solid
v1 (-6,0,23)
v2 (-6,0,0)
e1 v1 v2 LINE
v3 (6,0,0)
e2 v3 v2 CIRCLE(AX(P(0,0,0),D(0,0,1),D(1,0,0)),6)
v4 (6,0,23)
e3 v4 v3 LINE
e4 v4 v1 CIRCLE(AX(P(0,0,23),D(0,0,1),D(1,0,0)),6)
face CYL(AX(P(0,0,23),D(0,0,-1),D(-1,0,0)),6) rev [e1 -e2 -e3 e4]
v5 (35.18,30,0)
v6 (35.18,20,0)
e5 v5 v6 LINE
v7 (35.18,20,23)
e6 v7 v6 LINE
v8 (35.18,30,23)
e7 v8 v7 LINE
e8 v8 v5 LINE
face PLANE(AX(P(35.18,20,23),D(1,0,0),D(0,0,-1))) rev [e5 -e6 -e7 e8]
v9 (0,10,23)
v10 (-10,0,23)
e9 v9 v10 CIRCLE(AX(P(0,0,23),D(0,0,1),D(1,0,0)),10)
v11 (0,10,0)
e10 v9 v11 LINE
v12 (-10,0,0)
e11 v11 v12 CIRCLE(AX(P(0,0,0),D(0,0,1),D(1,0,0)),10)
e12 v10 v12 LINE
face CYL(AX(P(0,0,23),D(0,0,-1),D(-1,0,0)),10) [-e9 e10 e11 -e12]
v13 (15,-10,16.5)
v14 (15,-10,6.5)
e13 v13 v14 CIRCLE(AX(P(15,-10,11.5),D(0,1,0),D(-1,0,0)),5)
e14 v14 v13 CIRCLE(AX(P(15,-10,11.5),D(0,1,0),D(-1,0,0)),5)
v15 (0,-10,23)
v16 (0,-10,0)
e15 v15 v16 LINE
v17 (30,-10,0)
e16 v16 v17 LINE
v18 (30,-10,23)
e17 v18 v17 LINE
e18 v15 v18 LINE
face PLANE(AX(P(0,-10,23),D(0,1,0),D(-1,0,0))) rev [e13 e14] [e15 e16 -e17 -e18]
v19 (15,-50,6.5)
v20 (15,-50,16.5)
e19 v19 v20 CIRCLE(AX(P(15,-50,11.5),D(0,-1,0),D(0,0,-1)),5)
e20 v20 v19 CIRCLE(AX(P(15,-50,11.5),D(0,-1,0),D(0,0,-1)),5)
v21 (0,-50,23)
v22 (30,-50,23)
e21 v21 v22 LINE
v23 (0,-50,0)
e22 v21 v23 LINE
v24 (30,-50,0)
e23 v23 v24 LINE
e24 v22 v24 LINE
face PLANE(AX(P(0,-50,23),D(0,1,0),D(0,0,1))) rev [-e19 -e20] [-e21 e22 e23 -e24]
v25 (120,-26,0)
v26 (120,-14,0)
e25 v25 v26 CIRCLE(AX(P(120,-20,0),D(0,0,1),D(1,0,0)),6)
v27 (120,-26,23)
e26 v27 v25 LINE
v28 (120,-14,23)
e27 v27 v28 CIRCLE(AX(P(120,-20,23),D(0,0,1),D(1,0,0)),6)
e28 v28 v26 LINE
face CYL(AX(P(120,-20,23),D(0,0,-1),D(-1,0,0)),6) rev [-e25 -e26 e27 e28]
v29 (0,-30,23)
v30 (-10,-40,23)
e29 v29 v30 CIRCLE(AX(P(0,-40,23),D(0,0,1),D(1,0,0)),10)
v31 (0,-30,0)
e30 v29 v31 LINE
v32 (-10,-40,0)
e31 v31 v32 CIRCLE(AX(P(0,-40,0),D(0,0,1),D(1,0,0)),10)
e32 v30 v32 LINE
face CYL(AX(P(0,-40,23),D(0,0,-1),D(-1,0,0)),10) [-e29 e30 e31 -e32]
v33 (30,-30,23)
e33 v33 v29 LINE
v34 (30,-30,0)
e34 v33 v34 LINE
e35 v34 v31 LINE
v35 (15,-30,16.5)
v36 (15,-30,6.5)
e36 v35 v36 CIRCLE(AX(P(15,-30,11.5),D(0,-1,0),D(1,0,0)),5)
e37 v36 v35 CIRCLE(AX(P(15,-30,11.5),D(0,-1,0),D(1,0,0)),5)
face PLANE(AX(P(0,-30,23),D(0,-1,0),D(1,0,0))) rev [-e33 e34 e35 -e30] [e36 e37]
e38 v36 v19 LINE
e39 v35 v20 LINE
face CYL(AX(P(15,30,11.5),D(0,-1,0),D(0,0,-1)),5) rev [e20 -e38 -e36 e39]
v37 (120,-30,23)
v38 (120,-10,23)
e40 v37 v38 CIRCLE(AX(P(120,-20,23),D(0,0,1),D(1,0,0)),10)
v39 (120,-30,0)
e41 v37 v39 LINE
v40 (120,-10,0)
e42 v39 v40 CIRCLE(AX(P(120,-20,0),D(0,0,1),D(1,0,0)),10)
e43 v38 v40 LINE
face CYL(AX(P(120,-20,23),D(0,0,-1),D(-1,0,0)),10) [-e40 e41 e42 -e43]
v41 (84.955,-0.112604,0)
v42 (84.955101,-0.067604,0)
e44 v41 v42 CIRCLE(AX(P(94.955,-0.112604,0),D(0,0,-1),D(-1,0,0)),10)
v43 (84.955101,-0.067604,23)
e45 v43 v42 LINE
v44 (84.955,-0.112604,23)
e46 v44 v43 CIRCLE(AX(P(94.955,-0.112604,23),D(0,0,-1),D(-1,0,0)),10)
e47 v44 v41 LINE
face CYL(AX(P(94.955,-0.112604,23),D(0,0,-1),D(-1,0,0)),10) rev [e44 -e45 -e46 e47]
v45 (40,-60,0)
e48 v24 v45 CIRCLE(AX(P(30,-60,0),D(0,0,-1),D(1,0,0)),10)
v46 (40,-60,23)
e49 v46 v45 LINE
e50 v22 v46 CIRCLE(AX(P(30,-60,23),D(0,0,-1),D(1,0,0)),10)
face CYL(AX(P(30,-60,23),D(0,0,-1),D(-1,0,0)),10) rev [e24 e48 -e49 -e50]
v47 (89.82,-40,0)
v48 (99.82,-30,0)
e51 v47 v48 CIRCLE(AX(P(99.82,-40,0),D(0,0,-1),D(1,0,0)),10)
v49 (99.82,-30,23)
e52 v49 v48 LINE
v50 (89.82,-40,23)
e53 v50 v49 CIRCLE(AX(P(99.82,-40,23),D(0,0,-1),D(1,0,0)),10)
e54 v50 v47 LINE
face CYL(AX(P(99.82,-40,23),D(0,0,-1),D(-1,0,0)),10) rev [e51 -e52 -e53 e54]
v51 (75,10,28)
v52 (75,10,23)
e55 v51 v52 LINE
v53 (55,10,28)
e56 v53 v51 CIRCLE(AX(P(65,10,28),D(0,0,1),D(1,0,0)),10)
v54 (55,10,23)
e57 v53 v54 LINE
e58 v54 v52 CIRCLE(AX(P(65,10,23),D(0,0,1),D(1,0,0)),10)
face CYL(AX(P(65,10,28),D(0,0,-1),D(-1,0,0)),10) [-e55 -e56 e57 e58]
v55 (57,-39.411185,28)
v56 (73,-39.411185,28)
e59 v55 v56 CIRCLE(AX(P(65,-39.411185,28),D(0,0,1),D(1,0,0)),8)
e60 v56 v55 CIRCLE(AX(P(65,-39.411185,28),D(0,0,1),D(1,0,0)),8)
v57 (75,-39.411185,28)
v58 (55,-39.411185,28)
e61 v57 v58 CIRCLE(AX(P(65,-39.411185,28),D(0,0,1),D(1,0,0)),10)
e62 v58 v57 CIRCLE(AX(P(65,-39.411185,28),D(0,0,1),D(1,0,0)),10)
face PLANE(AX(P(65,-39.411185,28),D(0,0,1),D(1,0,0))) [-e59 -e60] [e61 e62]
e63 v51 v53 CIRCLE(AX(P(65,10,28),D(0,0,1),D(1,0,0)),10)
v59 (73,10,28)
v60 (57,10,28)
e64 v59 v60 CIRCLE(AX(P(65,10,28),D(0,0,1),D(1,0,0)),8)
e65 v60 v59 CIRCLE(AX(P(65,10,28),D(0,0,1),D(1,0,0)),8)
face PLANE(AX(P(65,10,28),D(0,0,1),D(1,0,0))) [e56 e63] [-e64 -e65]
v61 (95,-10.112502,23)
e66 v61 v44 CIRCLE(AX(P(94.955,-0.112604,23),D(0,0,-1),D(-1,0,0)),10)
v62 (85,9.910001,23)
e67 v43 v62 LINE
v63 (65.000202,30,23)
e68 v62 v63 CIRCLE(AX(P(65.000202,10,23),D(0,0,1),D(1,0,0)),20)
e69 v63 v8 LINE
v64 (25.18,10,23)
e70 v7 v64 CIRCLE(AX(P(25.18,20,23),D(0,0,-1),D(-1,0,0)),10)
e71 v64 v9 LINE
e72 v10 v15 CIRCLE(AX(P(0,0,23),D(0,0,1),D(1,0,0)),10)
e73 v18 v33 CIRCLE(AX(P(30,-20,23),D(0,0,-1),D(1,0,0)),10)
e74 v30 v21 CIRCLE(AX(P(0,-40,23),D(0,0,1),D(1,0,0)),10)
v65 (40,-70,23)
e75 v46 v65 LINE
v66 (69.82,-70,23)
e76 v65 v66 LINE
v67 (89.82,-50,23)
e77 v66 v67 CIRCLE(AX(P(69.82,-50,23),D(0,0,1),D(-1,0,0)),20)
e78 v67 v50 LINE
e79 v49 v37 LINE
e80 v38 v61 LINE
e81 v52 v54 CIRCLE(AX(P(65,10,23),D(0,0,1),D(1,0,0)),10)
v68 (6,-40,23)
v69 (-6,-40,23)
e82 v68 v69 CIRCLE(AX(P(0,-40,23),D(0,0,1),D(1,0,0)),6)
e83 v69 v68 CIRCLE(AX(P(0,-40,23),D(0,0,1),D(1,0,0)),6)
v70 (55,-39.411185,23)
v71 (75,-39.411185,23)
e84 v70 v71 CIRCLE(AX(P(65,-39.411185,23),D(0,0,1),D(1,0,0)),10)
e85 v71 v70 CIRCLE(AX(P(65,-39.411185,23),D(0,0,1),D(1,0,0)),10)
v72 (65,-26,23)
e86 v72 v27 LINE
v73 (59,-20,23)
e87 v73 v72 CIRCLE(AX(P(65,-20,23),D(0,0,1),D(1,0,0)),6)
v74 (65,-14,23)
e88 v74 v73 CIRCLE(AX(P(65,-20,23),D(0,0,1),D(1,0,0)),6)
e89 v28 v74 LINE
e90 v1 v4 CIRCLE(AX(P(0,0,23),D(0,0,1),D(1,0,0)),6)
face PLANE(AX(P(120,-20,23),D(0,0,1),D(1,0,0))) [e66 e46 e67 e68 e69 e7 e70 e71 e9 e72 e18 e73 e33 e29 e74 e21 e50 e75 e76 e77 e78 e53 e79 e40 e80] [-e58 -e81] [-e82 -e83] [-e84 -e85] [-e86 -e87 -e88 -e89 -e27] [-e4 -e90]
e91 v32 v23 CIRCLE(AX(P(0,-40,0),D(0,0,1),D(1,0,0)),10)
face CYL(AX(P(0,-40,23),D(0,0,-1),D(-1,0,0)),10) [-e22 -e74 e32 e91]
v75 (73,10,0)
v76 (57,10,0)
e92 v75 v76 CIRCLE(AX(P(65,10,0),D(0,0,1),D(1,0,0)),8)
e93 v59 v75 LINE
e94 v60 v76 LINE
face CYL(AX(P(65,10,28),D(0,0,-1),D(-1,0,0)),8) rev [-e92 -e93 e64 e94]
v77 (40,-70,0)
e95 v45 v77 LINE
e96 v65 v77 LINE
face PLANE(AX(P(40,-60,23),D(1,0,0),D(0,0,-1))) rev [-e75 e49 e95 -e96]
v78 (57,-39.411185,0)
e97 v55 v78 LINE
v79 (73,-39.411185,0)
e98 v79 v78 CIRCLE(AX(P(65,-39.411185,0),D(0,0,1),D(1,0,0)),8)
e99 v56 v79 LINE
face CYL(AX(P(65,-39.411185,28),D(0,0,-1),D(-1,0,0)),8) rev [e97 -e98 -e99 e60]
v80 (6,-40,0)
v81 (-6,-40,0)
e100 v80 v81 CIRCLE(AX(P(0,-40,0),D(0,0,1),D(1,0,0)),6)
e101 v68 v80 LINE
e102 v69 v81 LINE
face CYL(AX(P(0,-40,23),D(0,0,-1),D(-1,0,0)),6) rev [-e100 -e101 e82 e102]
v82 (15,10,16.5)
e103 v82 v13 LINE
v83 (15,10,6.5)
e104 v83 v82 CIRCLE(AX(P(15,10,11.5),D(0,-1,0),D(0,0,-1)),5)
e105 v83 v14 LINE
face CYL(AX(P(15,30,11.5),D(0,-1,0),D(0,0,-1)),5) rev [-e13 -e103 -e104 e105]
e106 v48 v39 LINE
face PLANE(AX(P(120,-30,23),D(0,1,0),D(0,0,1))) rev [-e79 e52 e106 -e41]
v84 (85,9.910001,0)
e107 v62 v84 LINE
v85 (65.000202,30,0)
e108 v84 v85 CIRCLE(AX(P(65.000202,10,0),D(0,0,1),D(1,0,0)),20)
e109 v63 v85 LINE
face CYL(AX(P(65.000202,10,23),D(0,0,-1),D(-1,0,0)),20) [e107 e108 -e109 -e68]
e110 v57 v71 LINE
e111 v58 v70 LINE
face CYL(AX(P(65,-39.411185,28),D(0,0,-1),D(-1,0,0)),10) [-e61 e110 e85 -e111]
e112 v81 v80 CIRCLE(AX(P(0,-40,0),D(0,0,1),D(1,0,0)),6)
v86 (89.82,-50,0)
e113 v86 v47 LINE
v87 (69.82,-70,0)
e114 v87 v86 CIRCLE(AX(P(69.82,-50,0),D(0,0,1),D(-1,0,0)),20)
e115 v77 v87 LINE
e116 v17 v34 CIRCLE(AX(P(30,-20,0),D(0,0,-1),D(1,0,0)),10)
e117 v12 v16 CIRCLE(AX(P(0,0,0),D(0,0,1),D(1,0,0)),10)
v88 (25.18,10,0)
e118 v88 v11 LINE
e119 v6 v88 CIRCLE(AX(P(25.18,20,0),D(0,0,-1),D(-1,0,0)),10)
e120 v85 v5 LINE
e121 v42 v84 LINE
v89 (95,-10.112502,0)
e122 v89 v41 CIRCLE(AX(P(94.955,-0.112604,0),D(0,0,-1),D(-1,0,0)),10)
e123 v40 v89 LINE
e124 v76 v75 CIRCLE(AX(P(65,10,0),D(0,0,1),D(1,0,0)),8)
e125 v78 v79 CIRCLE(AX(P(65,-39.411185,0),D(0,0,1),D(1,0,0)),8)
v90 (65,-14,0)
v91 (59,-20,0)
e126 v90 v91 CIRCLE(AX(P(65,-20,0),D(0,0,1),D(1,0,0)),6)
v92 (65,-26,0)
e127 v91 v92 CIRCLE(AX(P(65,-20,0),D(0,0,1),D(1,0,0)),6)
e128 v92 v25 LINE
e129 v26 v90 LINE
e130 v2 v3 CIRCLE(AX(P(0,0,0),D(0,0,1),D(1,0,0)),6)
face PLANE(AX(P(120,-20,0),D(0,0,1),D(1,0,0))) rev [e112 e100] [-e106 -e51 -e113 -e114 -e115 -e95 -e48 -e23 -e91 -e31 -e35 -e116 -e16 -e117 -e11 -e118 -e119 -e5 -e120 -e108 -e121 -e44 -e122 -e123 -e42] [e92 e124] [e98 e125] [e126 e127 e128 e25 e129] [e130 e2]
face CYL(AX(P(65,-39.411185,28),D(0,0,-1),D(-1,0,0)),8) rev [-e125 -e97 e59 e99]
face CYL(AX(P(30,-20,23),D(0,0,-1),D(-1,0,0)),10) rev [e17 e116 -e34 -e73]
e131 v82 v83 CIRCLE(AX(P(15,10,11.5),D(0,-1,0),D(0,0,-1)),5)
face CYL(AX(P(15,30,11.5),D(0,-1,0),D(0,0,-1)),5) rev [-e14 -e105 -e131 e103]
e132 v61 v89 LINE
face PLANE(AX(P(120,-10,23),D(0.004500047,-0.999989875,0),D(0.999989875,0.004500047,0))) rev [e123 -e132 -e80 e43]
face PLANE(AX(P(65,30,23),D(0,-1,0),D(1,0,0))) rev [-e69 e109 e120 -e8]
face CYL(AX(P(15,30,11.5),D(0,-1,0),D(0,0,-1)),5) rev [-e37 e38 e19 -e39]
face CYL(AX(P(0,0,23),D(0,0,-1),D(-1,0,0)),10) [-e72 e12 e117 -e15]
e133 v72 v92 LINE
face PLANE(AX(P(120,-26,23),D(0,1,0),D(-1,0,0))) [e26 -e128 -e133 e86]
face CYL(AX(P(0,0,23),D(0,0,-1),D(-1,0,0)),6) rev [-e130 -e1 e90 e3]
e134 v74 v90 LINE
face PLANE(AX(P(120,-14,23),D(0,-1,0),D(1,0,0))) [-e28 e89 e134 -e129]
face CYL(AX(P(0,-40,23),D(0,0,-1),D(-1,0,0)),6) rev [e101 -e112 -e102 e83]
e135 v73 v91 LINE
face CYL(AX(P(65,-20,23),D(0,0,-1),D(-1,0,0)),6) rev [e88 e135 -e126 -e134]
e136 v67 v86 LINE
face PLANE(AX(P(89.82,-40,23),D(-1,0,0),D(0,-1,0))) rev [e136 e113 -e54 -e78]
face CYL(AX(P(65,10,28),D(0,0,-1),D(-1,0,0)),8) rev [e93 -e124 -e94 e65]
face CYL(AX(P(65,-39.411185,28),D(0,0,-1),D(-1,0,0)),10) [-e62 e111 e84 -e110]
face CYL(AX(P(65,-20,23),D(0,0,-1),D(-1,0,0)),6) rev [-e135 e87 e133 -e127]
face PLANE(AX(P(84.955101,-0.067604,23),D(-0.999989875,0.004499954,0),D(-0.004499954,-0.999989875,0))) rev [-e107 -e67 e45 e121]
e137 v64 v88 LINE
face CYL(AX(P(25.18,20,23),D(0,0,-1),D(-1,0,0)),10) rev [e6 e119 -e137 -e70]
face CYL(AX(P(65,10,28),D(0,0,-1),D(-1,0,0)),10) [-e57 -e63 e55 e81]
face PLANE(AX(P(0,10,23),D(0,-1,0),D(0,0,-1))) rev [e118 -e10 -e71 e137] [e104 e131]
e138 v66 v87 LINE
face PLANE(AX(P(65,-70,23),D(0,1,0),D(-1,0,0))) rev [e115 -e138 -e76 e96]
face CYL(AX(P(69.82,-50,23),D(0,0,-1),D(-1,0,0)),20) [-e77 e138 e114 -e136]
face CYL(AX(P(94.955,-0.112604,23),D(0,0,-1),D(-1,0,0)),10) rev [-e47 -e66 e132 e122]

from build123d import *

# Parameters (mm, degrees)
BRACKET_PROFILE_SKETCH_R = 6
BRACKET_BASE_23MM_DEPTH  = 23
BOSS_PAD_SKETCH_R        = 10
BOSS_PAD_SKETCH_R_2      = 8
BOSS_PAD_5MM_DEPTH       = 5
HOLE_10_SKETCH_R         = 5
HOLE_10_DEPTH            = 156.190205877
PROFILE_CUT_SKETCH_R     = 8
PROFILE_CUT_DEPTH        = 150.428912865


with BuildPart() as part:
    # Bracket Profile Sketch → Bracket Base 23mm (new body)
    with BuildSketch(Plane.XY):
        with BuildLine():
            Line((65, -70), (40, -70))
            Line((40, -70), (40, -60))
            ThreePointArc((40, -60), (37.071067812, -52.928932188), (30, -50))
            Line((30, -50), (0, -50))
            ThreePointArc((0, -50), (-10, -40), (0, -30))
            Line((0, -30), (30, -30))
            ThreePointArc((30, -30), (40, -20), (30, -10))
            Line((30, -10), (0, -10))
            ThreePointArc((0, -10), (-10, 0), (0, 10))
            Line((0, 10), (25.18, 10))
            ThreePointArc((25.18, 10), (32.251067812, 12.928932188), (35.18, 20))
            Line((35.18, 20), (35.18, 30))
            Line((35.18, 30), (65, 30))
            ThreePointArc((65, 30), (79.174121887, 24.110280263), (85, 9.910000911))
            Line((85, 9.910000911), (84.955100778, -0.067604024))
            ThreePointArc((84.955100778, -0.067604024), (87.883932045, -7.183671708), (95, -10.112502316))
            Line((95, -10.112502316), (120, -10))
            ThreePointArc((120, -10), (130, -20), (120, -30))
            Line((120, -30), (99.82, -30))
            ThreePointArc((99.82, -30), (92.748932188, -32.928932188), (89.82, -40))
            Line((89.82, -40), (89.82, -50))
            ThreePointArc((89.82, -50), (83.962135624, -64.142135624), (69.82, -70))
            Line((69.82, -70), (65, -70))
        make_face()
        Circle(BRACKET_PROFILE_SKETCH_R, mode=Mode.SUBTRACT)
        with Locations((0, -40)):
            Circle(BRACKET_PROFILE_SKETCH_R, mode=Mode.SUBTRACT)
        with BuildLine():
            Line((120, -26), (65, -26))
            ThreePointArc((65, -26), (59, -20), (65, -14))
            Line((65, -14), (120, -14))
            ThreePointArc((120, -14), (126, -20), (120, -26))
        make_face(mode=Mode.SUBTRACT)
    extrude(amount=BRACKET_BASE_23MM_DEPTH)

    # Boss Pad Sketch → Boss Pad 5mm (add)
    # profile 1 of 2: a face of its own
    with BuildSketch(Plane.XY.offset(23)):
        with Locations((65, 10)):
            Circle(BOSS_PAD_SKETCH_R)
        with Locations((65, 10)):
            Circle(BOSS_PAD_SKETCH_R_2, mode=Mode.SUBTRACT)
    # profile 2 of 2: a face of its own
    with BuildSketch(Plane.XY.offset(23)):
        with Locations((65, -39.411185403)):
            Circle(BOSS_PAD_SKETCH_R)
        with Locations((65, -39.411185403)):
            Circle(BOSS_PAD_SKETCH_R_2, mode=Mode.SUBTRACT)
    extrude(amount=BOSS_PAD_5MM_DEPTH)

    # Hole Ø10 Sketch → Hole Ø10 (cut, through all)
    with BuildSketch(Plane.XZ.offset(50)):
        with Locations(Location((15, 11.5, 0), (0, 0, 270))):
            Circle(HOLE_10_SKETCH_R)
    extrude(amount=-HOLE_10_DEPTH, mode=Mode.SUBTRACT)

    # Profile Cut Sketch → Profile Cut (cut, through all)
    with BuildSketch(Plane.XY.offset(23)):
        with Locations((65, 10)):
            Circle(PROFILE_CUT_SKETCH_R)
        with Locations((65, -39.411185403)):
            Circle(PROFILE_CUT_SKETCH_R)
    extrude(amount=-PROFILE_CUT_DEPTH, mode=Mode.SUBTRACT)


solid = part.part
